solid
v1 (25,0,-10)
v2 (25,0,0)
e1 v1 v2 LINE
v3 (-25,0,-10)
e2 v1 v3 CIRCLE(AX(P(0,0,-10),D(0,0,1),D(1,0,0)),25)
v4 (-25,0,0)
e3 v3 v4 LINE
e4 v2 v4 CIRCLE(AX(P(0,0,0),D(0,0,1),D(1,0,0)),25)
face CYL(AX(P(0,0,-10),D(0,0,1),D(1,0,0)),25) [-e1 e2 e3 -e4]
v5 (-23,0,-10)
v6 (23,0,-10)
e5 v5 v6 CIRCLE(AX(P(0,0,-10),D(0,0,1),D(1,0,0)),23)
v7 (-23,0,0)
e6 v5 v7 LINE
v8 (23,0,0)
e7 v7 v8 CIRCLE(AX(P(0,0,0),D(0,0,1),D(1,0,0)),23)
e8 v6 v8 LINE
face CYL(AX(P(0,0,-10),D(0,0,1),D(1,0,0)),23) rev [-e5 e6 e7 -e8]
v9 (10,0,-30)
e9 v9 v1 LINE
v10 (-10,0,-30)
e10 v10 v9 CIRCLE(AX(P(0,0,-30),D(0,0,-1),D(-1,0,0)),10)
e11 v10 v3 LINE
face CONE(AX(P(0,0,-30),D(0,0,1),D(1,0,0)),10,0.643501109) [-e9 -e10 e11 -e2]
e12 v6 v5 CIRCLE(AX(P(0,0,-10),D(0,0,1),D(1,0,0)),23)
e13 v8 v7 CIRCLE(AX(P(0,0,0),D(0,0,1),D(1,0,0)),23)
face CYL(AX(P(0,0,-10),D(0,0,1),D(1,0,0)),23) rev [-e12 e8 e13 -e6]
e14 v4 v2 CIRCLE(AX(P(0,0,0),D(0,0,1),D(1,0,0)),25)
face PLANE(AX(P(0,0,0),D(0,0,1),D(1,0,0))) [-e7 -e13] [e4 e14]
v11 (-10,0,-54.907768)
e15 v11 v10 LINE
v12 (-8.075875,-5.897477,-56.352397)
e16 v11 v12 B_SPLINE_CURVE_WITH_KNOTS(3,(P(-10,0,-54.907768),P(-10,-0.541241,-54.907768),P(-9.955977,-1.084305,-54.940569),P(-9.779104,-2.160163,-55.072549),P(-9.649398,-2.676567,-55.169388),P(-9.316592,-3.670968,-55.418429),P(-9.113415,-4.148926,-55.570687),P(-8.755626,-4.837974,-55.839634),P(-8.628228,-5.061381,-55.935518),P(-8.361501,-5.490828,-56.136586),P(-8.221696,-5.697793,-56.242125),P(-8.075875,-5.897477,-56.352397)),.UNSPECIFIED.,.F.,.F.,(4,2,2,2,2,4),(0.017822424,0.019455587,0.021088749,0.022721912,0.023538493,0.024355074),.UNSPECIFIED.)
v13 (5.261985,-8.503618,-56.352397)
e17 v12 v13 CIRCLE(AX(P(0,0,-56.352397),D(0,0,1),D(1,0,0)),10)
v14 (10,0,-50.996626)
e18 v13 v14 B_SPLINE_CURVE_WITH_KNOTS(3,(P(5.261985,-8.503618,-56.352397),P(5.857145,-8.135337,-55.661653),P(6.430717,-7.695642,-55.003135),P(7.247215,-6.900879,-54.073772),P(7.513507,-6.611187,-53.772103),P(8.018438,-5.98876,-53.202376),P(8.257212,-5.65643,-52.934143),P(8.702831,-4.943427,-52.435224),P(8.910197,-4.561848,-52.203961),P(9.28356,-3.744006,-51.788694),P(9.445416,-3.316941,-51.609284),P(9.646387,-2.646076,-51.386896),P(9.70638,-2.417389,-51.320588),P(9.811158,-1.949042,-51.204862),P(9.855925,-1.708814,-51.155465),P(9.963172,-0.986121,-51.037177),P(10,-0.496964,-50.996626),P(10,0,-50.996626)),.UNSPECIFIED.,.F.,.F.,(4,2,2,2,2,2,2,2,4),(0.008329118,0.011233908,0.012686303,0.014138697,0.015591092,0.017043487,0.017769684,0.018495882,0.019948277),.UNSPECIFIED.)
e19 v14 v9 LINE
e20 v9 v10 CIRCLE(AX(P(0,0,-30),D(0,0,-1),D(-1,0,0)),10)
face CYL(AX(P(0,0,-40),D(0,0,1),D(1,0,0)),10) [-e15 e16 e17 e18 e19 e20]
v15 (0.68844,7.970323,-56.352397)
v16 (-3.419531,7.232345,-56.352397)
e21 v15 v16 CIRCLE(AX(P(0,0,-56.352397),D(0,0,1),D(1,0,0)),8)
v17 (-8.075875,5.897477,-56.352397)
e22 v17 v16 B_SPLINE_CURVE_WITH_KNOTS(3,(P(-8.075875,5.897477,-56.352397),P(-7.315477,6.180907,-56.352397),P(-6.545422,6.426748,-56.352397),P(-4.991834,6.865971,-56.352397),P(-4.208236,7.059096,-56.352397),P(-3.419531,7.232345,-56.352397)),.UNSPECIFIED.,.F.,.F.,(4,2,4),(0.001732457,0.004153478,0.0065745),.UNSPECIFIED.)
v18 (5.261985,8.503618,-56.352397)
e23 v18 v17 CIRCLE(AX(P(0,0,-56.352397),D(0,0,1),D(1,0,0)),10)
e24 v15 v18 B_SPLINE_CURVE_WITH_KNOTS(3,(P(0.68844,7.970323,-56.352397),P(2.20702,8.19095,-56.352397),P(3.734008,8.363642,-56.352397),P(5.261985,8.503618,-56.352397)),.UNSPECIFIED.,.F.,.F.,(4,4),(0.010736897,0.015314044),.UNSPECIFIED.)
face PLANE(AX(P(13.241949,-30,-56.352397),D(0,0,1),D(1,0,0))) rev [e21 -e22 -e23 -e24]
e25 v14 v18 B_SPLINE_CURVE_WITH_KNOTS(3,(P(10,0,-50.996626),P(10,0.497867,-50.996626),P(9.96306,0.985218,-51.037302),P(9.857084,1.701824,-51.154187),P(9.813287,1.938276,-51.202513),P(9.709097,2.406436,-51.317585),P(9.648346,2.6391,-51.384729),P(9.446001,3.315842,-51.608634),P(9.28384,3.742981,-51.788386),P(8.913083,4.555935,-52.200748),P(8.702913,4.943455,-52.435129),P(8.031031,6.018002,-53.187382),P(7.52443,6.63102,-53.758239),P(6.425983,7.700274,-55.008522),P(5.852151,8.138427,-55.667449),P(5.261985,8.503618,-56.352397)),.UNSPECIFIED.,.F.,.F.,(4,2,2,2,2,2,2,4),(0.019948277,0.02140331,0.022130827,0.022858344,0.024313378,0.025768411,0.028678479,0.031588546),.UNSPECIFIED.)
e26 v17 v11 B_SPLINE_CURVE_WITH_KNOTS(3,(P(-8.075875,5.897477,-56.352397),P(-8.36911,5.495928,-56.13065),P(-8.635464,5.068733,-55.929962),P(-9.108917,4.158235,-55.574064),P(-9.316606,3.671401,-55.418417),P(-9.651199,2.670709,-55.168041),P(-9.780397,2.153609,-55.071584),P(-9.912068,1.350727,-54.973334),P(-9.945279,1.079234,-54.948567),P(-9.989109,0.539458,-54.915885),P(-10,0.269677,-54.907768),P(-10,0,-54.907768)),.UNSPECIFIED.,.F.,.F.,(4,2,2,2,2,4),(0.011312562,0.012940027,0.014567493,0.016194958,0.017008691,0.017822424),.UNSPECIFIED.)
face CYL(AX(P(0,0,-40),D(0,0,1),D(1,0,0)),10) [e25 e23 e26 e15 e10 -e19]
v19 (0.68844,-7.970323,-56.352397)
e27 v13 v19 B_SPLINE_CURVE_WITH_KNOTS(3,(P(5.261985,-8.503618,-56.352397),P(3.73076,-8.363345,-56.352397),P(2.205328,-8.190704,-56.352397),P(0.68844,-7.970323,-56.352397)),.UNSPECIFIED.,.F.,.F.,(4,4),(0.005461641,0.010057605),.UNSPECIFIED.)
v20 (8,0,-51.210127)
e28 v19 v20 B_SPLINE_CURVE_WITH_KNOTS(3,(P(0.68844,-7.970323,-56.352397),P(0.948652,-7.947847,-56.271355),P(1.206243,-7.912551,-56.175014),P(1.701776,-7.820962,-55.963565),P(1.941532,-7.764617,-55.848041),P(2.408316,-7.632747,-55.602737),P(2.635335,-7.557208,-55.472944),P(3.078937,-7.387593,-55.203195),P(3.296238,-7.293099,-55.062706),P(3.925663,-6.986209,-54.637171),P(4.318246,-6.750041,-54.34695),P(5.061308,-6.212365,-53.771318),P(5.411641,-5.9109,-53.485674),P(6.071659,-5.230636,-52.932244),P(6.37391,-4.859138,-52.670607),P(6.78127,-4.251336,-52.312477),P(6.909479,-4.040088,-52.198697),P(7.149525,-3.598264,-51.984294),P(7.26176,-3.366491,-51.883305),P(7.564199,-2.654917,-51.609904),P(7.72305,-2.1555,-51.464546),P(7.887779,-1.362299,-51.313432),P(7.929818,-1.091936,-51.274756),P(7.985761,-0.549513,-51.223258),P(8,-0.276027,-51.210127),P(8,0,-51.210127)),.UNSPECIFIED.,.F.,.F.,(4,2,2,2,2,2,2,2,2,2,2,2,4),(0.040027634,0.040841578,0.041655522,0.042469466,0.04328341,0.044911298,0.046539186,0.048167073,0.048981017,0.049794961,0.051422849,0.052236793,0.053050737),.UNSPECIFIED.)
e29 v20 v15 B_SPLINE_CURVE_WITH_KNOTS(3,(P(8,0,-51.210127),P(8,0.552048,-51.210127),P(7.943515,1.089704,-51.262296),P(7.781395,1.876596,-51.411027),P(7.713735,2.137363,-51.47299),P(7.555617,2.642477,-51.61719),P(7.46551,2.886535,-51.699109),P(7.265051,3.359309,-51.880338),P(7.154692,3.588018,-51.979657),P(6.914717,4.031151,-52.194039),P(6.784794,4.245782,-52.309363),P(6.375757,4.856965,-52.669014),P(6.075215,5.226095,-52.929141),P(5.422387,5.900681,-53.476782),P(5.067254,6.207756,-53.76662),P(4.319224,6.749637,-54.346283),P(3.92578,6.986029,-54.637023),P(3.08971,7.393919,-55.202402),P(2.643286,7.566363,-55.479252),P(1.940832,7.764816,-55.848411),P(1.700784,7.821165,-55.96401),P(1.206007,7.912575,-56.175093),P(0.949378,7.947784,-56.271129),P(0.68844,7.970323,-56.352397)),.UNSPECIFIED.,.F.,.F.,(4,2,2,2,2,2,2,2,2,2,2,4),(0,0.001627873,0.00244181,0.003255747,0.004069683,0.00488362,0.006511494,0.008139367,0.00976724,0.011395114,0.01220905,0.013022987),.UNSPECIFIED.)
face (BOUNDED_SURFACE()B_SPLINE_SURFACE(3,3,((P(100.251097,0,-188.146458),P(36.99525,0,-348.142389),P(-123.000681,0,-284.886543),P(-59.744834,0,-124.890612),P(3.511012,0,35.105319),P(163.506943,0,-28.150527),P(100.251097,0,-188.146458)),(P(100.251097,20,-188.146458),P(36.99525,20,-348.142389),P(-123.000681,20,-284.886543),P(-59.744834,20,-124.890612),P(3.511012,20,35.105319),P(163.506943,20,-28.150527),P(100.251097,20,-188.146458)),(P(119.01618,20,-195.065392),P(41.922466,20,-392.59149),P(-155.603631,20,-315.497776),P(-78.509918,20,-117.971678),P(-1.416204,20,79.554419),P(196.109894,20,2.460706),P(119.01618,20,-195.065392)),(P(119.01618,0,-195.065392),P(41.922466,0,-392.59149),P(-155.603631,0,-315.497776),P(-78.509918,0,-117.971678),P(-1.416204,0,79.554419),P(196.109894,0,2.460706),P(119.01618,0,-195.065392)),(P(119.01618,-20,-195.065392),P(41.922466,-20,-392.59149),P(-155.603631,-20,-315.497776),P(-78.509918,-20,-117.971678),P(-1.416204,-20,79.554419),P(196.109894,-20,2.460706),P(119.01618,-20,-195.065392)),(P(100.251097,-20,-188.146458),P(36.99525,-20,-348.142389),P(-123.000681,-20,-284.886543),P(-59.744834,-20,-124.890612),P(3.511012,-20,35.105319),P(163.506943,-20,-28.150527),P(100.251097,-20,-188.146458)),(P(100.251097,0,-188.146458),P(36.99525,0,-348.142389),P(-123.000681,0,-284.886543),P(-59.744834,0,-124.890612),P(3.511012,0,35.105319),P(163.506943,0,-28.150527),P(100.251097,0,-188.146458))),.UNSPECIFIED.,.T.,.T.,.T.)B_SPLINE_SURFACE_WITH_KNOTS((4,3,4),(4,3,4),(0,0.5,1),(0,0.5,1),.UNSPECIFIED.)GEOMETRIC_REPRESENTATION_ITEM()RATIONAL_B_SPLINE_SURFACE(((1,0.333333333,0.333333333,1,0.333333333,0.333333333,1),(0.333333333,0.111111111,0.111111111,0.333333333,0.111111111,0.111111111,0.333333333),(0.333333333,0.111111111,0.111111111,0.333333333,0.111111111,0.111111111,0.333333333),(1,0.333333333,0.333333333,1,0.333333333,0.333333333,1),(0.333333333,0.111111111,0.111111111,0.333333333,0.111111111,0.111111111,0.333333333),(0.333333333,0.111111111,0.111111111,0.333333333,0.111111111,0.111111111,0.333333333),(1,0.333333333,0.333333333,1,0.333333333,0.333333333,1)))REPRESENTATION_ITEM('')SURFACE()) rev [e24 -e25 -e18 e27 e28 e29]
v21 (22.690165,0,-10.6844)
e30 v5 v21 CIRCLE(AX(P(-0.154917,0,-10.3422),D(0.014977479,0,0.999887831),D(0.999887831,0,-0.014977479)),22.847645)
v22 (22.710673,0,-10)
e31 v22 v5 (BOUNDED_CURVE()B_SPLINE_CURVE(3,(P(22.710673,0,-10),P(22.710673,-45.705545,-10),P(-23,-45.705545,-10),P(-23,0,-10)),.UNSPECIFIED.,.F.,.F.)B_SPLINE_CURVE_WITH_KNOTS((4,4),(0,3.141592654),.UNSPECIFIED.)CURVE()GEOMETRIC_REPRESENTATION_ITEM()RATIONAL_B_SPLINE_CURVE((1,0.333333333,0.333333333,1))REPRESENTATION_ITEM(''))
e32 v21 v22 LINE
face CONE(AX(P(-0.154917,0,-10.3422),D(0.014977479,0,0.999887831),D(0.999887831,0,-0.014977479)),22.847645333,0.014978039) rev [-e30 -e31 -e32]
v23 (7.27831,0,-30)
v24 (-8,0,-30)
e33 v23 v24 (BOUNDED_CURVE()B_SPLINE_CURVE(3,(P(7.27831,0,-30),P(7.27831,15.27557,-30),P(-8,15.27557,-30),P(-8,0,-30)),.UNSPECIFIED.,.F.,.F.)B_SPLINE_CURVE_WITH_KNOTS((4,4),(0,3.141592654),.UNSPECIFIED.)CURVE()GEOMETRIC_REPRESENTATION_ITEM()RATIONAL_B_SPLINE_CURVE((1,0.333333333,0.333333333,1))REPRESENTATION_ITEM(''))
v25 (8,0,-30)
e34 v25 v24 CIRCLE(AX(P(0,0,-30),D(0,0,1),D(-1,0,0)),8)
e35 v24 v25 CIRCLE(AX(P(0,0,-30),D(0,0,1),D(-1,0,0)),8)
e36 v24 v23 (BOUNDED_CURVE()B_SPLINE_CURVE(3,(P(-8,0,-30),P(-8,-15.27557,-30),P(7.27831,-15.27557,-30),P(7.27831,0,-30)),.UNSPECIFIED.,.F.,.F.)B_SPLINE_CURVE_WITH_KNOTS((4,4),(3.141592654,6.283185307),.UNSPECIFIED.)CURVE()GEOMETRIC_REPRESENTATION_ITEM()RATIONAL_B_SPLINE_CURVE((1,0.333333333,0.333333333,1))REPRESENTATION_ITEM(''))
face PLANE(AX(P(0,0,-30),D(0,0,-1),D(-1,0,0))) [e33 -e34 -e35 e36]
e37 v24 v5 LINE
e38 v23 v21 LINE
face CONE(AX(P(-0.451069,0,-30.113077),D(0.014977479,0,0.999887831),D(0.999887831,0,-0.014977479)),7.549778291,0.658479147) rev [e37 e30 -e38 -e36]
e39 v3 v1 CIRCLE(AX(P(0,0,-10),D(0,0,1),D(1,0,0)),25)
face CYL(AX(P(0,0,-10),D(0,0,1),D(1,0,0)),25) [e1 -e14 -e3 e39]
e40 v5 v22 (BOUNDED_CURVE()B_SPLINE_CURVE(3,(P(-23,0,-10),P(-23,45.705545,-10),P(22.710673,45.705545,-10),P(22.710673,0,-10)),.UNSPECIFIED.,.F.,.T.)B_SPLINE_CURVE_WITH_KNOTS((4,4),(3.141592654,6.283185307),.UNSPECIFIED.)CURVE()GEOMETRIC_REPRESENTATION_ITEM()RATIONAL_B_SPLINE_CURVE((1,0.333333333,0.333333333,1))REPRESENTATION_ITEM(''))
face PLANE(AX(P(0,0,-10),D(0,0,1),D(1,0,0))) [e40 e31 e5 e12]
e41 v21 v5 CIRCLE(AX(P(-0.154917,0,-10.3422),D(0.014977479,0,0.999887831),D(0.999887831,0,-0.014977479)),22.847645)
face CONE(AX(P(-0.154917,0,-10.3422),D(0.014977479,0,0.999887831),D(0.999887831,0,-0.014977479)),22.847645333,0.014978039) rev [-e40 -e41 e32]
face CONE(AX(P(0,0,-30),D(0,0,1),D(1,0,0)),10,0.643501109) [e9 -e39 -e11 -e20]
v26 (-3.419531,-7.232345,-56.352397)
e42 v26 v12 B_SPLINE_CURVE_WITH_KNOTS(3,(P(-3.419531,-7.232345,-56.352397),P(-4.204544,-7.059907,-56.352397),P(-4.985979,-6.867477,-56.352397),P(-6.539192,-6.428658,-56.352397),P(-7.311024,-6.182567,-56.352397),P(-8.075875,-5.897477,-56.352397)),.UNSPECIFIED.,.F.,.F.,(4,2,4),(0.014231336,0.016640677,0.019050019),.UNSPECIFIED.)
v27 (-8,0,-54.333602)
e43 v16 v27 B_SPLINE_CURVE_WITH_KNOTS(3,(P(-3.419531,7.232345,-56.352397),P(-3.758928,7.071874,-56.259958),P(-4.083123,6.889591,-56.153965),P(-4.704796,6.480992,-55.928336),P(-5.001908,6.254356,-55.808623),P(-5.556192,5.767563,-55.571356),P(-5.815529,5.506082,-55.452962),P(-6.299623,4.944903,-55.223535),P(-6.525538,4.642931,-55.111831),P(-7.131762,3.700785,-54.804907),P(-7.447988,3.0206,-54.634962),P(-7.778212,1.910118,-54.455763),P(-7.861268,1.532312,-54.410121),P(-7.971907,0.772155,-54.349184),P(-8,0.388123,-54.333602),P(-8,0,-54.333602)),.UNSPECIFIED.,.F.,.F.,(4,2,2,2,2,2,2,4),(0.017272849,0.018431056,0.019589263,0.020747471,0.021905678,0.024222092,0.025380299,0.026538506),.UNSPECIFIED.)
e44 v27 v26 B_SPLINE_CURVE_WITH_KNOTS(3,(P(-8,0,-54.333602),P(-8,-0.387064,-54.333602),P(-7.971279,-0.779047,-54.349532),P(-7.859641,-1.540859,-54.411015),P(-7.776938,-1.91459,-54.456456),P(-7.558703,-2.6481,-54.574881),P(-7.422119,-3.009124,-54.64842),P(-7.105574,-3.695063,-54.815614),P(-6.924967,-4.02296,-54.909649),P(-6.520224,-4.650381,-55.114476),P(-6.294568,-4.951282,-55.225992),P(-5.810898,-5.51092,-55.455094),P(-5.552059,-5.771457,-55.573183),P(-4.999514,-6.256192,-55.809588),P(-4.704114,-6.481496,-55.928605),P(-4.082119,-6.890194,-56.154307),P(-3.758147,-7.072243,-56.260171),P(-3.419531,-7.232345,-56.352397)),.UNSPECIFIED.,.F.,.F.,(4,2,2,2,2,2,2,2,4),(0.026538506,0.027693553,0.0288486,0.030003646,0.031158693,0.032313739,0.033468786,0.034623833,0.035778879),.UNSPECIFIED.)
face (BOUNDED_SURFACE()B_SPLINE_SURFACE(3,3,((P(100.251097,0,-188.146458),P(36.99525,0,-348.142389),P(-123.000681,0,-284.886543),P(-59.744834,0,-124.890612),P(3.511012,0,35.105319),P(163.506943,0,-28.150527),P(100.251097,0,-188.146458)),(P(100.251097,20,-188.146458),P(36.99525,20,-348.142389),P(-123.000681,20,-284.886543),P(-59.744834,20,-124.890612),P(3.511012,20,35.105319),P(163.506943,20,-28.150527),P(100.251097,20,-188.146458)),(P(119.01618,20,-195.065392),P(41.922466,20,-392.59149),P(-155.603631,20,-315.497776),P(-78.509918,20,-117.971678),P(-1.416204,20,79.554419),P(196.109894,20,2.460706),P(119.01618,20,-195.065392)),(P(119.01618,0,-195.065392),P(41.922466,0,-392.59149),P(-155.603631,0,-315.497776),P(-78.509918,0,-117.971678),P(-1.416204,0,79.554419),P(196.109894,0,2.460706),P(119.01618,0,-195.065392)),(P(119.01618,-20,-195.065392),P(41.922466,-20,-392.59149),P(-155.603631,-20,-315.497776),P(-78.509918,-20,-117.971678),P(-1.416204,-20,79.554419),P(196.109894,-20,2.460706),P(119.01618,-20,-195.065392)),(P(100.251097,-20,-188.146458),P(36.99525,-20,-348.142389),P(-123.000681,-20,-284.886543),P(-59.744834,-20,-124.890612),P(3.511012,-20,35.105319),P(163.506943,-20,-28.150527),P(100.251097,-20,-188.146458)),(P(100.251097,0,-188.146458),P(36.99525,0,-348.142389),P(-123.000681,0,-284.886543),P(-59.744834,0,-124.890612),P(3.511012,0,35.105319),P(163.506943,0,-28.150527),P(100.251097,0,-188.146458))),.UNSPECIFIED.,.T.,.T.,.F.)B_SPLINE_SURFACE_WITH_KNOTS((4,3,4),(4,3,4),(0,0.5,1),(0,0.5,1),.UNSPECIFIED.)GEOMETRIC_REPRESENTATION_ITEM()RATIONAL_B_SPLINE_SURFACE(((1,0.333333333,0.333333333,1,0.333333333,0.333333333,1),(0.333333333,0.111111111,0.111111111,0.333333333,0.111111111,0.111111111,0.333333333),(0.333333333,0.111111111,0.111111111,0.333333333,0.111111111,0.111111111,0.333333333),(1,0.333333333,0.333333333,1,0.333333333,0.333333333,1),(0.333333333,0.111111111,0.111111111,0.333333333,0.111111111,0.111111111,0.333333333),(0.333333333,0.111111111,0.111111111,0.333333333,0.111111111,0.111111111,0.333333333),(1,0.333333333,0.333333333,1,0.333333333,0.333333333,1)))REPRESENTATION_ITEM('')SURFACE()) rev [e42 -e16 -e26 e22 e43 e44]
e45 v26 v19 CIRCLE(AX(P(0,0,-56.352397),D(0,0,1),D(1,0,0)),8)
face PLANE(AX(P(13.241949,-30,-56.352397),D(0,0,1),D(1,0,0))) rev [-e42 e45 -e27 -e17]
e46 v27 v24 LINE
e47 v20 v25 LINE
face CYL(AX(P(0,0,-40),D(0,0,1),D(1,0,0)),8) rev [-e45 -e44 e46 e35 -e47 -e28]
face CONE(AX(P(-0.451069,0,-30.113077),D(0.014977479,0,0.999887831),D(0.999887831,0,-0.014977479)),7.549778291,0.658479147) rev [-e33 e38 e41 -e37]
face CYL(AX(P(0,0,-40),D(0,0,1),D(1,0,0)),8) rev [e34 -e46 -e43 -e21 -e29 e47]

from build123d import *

# Parameters (mm, degrees)
SKETCH_1_R          = 25.000000000000025
SKETCH_1_R_2        = 23.00000000000003
EXTRUDE_1_DEPTH     = 10
SKETCH_2_R          = 10
SKETCH_2_R_2        = 8
EXTRUDE_2_DEPTH     = 10
SKETCH_5_R          = 10
SKETCH_5_R_2        = 8
EXTRUDE_3_DEPTH     = 60
SKETCH_7_R          = 10.000000000000009
CUT_EXTRUDE_1_DEPTH = 30


with BuildPart() as part:
    # 草图1 → 凸台-拉伸1 (new body)
    with BuildSketch(Plane.XY):
        Circle(SKETCH_1_R)
        Circle(SKETCH_1_R_2, mode=Mode.SUBTRACT)
    extrude(amount=-EXTRUDE_1_DEPTH)



with BuildPart() as body_2:
    # 草图2 → 凸台-拉伸2 (new body)
    with BuildSketch(Plane(origin=(0, 0, -30), x_dir=(-1, 0, 0), z_dir=(0, 0, -1))):
        Circle(SKETCH_2_R)
        Circle(SKETCH_2_R_2, mode=Mode.SUBTRACT)
    extrude(amount=EXTRUDE_2_DEPTH)


with BuildPart() as part_1:
    add(part.part)

    add(body_2.part)  # loft_1 joins it to this body
    # loft up to a face of the part (loft_1)
    loft([Face(Wire([part_1.edges().sort_by_distance((-17.113677648, -18.224215686, -10))[0]])), Face(Wire([part_1.edges().sort_by_distance((6.845471059, -7.289686274, -30))[0]]))])

    # 草图5 → 凸台-拉伸3 (add)
    with BuildSketch(Plane(origin=(0, 0, -40), x_dir=(-1, 0, 0), z_dir=(0, 0, -1))):
        Circle(SKETCH_5_R)
        Circle(SKETCH_5_R_2, mode=Mode.SUBTRACT)
    extrude(amount=EXTRUDE_3_DEPTH)

    # 切除-扫描1: sweep along a path in 草图6
    with BuildLine(Plane(origin=(567.6487610779214, 3.3307e-13, 477.55598041107464), x_dir=(-0.9189626632299163, 0, 0.394344549333929), z_dir=(-1e-16, 1, 0))) as sweep_1_path:
        CenterArc((252.99231689471313, -798.553288549715), 96.02083107326227, 0, 360)
    # 草图7 → 切除-扫描1 (sweep, cut)
    with BuildSketch(Plane(origin=(-49.07172931438322, -6.26e-15, -133.08916371965483), x_dir=(-0.9382541725249339, 0, 0.3459466833770077), z_dir=(-0.3459466833770076, 0, -0.9382541725249338))):
        with Locations((-169.14965286891908, 3.3044e-13)):
            Circle(SKETCH_7_R)
    sweep(path=sweep_1_path.line, mode=Mode.SUBTRACT)


with BuildPart() as sweep_1_piece_1:
    # of the separate pieces the step leaves, piece 1, a body of its own (sweep_1_pieces)
    add(part_1.part.solids().sort_by_distance((25, 0, 0))[0])


with BuildPart() as sweep_1_piece_2:
    # of the separate pieces the step leaves, piece 2, a body of its own (sweep_1_pieces)
    add(part_1.part.solids().sort_by_distance((-10, 0, -75.99060176))[0])


with BuildPart() as cut_extrude_1_tool:
    # 草图9 → 切除-拉伸1 (new, symmetric)
    with BuildSketch(Plane(origin=(567.6487610779214, 3.3307e-13, 477.55598041107464), x_dir=(-0.9189626632299163, 0, 0.394344549333929), z_dir=(-1e-16, 1, 0))):
        Polygon((298.93530182729927, -709.2691688884134), (322.9434794568931, -719.5715395575278), (328.1692822059597, -736.3309694794536), (310.61737349860726, -766.3763892056517), (277.35748759673646, -755.1877218619298), (295.795407688748, -719.5715395575278), align=None)
    extrude(amount=CUT_EXTRUDE_1_DEPTH, both=True)


with BuildPart() as sweep_1_piece_1_1:
    add(sweep_1_piece_1.part)

    # 切除-拉伸1: cut by cut_extrude_1_tool
    add(cut_extrude_1_tool.part, mode=Mode.SUBTRACT)

    # 草图10 → 切除-旋转1 (revolve, cut)
    with BuildSketch(Plane(origin=(0, 0, 0), x_dir=(1, 0, 0), z_dir=(0, 1, 0))):
        Polygon((-23, 10), (-23, 0), (0, 0), (-0.8138721873565125, 54.3336376298419), (-7.9999999999999725, 54.3336376298419), (-7.9999999999999725, 30), align=None)
    revolve(axis=Axis((0, 0, 0), (-0.014977478627436109, 0, -0.9998878312760711)), mode=Mode.SUBTRACT)


with BuildPart() as sweep_1_piece_2_1:
    add(sweep_1_piece_2.part)

    # 切除-拉伸1: cut by cut_extrude_1_tool
    add(cut_extrude_1_tool.part, mode=Mode.SUBTRACT)


solid = sweep_1_piece_1_1.part
